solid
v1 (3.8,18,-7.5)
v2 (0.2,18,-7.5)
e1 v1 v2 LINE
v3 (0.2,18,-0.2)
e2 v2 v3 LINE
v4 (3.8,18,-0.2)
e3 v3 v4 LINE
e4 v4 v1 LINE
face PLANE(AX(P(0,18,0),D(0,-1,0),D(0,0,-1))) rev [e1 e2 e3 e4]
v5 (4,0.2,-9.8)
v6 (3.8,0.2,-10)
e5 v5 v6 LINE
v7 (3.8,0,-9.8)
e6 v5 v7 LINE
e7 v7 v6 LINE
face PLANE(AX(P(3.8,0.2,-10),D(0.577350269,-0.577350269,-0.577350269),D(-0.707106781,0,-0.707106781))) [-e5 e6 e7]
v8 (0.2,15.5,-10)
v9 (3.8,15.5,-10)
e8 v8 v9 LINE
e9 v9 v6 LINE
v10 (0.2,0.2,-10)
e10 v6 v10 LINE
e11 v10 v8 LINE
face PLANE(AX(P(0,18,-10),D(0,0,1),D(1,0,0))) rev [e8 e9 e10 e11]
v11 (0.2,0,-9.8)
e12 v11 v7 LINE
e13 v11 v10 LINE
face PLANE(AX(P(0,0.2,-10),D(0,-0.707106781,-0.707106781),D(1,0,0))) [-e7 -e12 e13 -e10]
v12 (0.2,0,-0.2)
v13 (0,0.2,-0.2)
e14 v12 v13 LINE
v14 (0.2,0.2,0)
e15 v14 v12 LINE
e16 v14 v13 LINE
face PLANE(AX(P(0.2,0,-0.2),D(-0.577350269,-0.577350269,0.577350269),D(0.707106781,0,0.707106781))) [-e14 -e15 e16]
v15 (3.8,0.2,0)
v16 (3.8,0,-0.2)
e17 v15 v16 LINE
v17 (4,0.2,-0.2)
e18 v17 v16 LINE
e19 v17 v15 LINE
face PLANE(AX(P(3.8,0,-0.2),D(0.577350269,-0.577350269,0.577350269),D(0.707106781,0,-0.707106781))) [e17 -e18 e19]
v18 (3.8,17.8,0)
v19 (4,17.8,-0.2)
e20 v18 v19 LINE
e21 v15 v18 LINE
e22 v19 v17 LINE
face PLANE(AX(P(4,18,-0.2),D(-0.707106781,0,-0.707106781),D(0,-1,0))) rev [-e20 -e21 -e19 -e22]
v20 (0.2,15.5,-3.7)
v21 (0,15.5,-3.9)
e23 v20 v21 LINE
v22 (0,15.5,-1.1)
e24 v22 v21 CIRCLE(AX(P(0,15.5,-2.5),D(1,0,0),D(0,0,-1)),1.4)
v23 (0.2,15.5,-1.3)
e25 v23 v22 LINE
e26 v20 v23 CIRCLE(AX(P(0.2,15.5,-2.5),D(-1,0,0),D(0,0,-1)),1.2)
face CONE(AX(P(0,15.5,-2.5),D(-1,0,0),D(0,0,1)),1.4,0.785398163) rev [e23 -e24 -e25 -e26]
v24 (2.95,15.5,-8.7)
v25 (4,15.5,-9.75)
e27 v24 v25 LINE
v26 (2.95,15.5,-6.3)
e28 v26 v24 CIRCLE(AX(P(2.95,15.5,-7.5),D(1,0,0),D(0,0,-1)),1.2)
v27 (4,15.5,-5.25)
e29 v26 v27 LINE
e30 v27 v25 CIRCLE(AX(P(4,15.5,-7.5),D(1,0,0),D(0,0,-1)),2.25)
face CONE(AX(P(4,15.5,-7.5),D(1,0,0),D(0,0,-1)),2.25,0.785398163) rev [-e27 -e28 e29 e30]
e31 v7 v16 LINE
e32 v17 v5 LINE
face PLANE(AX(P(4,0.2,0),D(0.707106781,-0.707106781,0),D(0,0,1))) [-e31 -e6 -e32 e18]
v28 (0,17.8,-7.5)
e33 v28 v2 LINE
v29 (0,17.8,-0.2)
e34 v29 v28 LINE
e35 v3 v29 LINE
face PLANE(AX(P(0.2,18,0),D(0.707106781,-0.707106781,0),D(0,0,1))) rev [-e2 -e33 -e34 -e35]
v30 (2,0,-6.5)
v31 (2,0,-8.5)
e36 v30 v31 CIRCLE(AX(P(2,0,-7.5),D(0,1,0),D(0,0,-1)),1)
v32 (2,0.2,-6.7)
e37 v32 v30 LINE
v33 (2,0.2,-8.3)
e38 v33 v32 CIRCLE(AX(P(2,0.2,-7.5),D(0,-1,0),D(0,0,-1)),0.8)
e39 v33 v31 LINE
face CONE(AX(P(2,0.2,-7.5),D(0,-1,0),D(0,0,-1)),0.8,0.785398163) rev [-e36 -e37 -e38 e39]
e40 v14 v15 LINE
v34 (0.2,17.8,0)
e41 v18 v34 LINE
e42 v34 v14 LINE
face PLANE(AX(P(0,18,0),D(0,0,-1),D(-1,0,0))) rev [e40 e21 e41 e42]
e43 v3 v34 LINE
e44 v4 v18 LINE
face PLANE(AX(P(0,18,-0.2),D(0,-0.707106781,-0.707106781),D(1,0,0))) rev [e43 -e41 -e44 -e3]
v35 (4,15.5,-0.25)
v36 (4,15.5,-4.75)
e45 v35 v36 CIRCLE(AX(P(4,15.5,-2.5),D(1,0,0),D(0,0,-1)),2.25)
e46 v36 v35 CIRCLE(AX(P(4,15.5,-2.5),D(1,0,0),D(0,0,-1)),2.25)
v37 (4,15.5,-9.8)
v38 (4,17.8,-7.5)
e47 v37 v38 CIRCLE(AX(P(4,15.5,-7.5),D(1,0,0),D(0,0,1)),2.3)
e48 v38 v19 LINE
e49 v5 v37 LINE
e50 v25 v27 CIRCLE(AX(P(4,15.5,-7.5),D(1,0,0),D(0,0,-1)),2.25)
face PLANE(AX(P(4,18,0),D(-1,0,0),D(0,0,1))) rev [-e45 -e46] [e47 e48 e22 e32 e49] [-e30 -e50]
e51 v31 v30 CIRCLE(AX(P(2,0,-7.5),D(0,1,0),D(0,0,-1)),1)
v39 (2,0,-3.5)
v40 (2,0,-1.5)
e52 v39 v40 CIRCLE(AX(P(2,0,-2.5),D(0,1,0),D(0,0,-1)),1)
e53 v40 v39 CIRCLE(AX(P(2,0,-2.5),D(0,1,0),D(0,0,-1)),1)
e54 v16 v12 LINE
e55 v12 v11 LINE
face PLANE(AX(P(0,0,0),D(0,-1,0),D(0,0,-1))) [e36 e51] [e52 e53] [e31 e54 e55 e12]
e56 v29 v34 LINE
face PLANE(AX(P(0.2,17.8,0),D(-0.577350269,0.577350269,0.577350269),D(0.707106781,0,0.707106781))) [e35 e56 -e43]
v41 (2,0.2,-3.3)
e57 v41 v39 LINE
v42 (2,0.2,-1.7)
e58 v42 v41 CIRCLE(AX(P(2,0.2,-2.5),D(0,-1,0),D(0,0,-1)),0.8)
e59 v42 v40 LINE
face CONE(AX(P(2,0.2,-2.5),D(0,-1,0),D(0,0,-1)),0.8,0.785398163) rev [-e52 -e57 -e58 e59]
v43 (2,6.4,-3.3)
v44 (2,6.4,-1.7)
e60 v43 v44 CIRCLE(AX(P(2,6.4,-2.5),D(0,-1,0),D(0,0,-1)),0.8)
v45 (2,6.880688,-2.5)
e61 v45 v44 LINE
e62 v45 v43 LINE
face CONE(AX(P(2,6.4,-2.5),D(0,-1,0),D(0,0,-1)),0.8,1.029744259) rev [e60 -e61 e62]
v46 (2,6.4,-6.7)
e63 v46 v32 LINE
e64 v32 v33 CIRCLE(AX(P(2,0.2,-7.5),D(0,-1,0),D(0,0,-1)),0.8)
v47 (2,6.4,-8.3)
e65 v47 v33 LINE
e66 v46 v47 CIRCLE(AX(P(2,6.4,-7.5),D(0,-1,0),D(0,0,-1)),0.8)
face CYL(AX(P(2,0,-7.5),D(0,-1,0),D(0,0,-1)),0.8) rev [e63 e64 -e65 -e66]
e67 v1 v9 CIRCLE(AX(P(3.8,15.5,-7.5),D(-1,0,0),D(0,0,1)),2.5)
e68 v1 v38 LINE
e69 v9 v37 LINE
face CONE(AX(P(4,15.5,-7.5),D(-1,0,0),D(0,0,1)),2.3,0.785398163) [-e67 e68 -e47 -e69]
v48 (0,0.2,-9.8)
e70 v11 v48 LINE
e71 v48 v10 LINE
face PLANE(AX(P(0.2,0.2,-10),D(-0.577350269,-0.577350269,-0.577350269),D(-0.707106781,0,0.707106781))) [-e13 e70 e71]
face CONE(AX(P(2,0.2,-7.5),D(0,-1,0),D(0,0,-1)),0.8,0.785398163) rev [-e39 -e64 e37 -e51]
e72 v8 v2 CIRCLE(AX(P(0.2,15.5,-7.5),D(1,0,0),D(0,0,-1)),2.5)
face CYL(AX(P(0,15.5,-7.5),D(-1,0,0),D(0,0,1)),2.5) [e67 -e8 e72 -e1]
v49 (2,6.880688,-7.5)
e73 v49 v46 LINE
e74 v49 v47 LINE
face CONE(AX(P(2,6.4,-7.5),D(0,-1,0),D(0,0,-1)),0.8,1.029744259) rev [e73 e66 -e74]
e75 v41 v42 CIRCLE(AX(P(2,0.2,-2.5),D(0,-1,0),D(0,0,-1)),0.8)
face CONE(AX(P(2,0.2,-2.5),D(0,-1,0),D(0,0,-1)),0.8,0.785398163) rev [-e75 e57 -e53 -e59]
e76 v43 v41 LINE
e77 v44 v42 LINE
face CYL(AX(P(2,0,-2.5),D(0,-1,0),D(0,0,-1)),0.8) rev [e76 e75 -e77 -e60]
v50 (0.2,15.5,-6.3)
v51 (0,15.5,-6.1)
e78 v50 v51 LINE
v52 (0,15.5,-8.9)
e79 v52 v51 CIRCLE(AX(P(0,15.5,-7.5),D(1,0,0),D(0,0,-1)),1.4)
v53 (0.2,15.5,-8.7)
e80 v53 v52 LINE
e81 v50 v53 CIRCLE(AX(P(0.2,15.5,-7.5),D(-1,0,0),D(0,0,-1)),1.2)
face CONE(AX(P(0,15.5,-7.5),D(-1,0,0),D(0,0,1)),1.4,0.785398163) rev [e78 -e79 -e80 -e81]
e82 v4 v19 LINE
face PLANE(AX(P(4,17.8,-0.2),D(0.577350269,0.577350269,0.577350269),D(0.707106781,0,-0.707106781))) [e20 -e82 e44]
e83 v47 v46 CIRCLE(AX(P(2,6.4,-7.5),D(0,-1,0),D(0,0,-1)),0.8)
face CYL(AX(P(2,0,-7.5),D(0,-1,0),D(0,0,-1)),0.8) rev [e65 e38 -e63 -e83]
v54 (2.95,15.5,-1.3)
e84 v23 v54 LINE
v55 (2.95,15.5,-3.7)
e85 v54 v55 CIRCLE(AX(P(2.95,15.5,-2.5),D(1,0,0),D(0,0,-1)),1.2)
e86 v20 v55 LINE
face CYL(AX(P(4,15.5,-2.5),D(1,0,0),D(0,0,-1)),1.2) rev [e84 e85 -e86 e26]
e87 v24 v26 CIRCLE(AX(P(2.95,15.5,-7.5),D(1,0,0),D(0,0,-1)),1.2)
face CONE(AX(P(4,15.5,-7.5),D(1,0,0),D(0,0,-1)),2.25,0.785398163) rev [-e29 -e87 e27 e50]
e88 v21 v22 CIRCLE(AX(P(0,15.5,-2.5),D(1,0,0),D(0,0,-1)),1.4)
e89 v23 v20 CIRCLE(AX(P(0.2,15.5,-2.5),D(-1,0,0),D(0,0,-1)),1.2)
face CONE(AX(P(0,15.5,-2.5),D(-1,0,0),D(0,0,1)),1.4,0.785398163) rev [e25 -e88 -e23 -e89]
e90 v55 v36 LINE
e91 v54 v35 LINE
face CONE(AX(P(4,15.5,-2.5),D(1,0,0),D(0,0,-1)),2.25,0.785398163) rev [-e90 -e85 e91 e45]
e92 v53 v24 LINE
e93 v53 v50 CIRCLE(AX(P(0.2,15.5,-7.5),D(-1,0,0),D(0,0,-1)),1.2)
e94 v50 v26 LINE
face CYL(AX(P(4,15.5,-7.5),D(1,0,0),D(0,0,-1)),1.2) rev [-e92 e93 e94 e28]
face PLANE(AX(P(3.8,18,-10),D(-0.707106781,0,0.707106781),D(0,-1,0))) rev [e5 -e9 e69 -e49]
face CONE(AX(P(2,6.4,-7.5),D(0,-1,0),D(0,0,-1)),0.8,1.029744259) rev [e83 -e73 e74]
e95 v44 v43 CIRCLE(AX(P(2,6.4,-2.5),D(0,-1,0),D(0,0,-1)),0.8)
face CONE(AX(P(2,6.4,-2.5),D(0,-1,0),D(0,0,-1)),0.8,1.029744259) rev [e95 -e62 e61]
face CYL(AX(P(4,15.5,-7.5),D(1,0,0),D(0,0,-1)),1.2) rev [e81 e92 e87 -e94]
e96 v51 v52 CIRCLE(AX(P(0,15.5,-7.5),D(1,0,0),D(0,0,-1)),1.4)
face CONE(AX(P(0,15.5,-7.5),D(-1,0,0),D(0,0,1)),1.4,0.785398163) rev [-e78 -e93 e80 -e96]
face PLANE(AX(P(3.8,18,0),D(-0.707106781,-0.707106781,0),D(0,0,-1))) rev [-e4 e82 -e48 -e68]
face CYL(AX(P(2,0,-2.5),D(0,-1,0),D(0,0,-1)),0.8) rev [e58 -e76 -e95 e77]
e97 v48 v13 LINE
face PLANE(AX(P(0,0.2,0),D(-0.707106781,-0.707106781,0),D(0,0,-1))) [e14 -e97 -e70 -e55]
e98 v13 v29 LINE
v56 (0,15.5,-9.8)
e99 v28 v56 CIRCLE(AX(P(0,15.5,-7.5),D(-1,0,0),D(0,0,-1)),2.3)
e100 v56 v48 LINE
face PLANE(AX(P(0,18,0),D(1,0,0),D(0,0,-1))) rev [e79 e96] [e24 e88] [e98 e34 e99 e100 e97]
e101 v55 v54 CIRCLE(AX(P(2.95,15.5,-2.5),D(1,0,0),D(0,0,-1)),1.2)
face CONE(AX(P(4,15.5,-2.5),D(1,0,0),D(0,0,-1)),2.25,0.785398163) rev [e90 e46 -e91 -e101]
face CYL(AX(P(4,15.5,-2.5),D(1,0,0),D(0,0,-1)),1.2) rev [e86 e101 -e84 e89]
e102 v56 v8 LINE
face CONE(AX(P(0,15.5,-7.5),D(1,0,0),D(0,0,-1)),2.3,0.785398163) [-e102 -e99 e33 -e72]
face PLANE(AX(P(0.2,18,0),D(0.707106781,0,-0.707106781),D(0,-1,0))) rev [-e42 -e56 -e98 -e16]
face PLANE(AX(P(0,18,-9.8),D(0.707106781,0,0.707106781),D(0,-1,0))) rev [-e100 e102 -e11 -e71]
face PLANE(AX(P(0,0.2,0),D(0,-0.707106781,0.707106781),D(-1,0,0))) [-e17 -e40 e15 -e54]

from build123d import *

# Parameters (mm, degrees)
SKETCH1_W                                            = 4
SKETCH1_H                                            = 10
BOSS_EXTRUDE1_DEPTH                                  = 18
HOLE_SIZE_SLOTTED_COUNTERSUNK_WOOD_SCREW_D           = 2.4
HOLE_SIZE_SLOTTED_COUNTERSUNK_WOOD_SCREW_CSINK_D     = 4.5
HOLE_SIZE_SLOTTED_COUNTERSUNK_WOOD_SCREW_CSINK_ANGLE = 90
M2_TAPPED_HOLE1_D                                    = 1.6
M2_TAPPED_HOLE1_DEPTH                                = 6.4
M2_TAPPED_HOLE1_TIP                                  = 0.480688495
FILLET1_R                                            = 2.5
CHAMFER1_SIZE                                        = 0.2


with BuildPart() as part:
    # Sketch1 → Boss-Extrude1 (new body)
    with BuildSketch(Plane(origin=(0, 0, 0), x_dir=(1, 0, 0), z_dir=(0, 1, 0))):
        with Locations((2, 5)):
            Rectangle(SKETCH1_W, SKETCH1_H)
    extrude(amount=BOSS_EXTRUDE1_DEPTH)

    # Hole size slotted countersunk wood screw type 1 (through all)
    with Locations(Plane(origin=(4, 0, 0), x_dir=(0, 0, -1), z_dir=(1, 0, 0))):
        with Locations((2.5, 15.5), (7.5, 15.5)):
            CounterSinkHole(HOLE_SIZE_SLOTTED_COUNTERSUNK_WOOD_SCREW_D / 2, HOLE_SIZE_SLOTTED_COUNTERSUNK_WOOD_SCREW_CSINK_D / 2, counter_sink_angle=HOLE_SIZE_SLOTTED_COUNTERSUNK_WOOD_SCREW_CSINK_ANGLE)

    # M2 Tapped Hole1
    with Locations(Plane(origin=(0, 0, 0), x_dir=(-1, 0, 0), z_dir=(0, -1, 0))):
        with Locations((-2, 2.5), (-2, 7.5)):
            Hole(M2_TAPPED_HOLE1_D / 2, depth=M2_TAPPED_HOLE1_DEPTH)
            with Locations((0, 0, -(M2_TAPPED_HOLE1_DEPTH + M2_TAPPED_HOLE1_TIP / 2))):  # 118° drill point
                Cone(0, M2_TAPPED_HOLE1_D / 2, M2_TAPPED_HOLE1_TIP, mode=Mode.SUBTRACT)

    # Fillet1
    fillet1_edges = [part.edges().sort_by_distance(p)[0] for p in [
        (2, 18, -10),
    ]]
    fillet(fillet1_edges, radius=FILLET1_R)

    # Chamfer1
    chamfer1_edges = [part.edges().sort_by_distance(p)[0] for p in [
        (4, 18, -3.75),
        (0, 15.5, -8.7),
        (0, 15.5, -3.7),
        (1.2, 0, -7.5),
        (1.2, 0, -2.5),
        (0, 18, -3.75),
        (0, 7.75, -10),
        (0, 17.267766953, -9.267766953),
        (4, 7.75, -10),
        (4, 17.267766953, -9.267766953),
        (2, 0, -10),
        (4, 0, -5),
        (2, 0, 0),
        (0, 0, -5),
        (4, 9, 0),
        (0, 9, 0),
        (2, 18, 0),
    ]]
    chamfer(chamfer1_edges, length=CHAMFER1_SIZE)


solid = part.part
